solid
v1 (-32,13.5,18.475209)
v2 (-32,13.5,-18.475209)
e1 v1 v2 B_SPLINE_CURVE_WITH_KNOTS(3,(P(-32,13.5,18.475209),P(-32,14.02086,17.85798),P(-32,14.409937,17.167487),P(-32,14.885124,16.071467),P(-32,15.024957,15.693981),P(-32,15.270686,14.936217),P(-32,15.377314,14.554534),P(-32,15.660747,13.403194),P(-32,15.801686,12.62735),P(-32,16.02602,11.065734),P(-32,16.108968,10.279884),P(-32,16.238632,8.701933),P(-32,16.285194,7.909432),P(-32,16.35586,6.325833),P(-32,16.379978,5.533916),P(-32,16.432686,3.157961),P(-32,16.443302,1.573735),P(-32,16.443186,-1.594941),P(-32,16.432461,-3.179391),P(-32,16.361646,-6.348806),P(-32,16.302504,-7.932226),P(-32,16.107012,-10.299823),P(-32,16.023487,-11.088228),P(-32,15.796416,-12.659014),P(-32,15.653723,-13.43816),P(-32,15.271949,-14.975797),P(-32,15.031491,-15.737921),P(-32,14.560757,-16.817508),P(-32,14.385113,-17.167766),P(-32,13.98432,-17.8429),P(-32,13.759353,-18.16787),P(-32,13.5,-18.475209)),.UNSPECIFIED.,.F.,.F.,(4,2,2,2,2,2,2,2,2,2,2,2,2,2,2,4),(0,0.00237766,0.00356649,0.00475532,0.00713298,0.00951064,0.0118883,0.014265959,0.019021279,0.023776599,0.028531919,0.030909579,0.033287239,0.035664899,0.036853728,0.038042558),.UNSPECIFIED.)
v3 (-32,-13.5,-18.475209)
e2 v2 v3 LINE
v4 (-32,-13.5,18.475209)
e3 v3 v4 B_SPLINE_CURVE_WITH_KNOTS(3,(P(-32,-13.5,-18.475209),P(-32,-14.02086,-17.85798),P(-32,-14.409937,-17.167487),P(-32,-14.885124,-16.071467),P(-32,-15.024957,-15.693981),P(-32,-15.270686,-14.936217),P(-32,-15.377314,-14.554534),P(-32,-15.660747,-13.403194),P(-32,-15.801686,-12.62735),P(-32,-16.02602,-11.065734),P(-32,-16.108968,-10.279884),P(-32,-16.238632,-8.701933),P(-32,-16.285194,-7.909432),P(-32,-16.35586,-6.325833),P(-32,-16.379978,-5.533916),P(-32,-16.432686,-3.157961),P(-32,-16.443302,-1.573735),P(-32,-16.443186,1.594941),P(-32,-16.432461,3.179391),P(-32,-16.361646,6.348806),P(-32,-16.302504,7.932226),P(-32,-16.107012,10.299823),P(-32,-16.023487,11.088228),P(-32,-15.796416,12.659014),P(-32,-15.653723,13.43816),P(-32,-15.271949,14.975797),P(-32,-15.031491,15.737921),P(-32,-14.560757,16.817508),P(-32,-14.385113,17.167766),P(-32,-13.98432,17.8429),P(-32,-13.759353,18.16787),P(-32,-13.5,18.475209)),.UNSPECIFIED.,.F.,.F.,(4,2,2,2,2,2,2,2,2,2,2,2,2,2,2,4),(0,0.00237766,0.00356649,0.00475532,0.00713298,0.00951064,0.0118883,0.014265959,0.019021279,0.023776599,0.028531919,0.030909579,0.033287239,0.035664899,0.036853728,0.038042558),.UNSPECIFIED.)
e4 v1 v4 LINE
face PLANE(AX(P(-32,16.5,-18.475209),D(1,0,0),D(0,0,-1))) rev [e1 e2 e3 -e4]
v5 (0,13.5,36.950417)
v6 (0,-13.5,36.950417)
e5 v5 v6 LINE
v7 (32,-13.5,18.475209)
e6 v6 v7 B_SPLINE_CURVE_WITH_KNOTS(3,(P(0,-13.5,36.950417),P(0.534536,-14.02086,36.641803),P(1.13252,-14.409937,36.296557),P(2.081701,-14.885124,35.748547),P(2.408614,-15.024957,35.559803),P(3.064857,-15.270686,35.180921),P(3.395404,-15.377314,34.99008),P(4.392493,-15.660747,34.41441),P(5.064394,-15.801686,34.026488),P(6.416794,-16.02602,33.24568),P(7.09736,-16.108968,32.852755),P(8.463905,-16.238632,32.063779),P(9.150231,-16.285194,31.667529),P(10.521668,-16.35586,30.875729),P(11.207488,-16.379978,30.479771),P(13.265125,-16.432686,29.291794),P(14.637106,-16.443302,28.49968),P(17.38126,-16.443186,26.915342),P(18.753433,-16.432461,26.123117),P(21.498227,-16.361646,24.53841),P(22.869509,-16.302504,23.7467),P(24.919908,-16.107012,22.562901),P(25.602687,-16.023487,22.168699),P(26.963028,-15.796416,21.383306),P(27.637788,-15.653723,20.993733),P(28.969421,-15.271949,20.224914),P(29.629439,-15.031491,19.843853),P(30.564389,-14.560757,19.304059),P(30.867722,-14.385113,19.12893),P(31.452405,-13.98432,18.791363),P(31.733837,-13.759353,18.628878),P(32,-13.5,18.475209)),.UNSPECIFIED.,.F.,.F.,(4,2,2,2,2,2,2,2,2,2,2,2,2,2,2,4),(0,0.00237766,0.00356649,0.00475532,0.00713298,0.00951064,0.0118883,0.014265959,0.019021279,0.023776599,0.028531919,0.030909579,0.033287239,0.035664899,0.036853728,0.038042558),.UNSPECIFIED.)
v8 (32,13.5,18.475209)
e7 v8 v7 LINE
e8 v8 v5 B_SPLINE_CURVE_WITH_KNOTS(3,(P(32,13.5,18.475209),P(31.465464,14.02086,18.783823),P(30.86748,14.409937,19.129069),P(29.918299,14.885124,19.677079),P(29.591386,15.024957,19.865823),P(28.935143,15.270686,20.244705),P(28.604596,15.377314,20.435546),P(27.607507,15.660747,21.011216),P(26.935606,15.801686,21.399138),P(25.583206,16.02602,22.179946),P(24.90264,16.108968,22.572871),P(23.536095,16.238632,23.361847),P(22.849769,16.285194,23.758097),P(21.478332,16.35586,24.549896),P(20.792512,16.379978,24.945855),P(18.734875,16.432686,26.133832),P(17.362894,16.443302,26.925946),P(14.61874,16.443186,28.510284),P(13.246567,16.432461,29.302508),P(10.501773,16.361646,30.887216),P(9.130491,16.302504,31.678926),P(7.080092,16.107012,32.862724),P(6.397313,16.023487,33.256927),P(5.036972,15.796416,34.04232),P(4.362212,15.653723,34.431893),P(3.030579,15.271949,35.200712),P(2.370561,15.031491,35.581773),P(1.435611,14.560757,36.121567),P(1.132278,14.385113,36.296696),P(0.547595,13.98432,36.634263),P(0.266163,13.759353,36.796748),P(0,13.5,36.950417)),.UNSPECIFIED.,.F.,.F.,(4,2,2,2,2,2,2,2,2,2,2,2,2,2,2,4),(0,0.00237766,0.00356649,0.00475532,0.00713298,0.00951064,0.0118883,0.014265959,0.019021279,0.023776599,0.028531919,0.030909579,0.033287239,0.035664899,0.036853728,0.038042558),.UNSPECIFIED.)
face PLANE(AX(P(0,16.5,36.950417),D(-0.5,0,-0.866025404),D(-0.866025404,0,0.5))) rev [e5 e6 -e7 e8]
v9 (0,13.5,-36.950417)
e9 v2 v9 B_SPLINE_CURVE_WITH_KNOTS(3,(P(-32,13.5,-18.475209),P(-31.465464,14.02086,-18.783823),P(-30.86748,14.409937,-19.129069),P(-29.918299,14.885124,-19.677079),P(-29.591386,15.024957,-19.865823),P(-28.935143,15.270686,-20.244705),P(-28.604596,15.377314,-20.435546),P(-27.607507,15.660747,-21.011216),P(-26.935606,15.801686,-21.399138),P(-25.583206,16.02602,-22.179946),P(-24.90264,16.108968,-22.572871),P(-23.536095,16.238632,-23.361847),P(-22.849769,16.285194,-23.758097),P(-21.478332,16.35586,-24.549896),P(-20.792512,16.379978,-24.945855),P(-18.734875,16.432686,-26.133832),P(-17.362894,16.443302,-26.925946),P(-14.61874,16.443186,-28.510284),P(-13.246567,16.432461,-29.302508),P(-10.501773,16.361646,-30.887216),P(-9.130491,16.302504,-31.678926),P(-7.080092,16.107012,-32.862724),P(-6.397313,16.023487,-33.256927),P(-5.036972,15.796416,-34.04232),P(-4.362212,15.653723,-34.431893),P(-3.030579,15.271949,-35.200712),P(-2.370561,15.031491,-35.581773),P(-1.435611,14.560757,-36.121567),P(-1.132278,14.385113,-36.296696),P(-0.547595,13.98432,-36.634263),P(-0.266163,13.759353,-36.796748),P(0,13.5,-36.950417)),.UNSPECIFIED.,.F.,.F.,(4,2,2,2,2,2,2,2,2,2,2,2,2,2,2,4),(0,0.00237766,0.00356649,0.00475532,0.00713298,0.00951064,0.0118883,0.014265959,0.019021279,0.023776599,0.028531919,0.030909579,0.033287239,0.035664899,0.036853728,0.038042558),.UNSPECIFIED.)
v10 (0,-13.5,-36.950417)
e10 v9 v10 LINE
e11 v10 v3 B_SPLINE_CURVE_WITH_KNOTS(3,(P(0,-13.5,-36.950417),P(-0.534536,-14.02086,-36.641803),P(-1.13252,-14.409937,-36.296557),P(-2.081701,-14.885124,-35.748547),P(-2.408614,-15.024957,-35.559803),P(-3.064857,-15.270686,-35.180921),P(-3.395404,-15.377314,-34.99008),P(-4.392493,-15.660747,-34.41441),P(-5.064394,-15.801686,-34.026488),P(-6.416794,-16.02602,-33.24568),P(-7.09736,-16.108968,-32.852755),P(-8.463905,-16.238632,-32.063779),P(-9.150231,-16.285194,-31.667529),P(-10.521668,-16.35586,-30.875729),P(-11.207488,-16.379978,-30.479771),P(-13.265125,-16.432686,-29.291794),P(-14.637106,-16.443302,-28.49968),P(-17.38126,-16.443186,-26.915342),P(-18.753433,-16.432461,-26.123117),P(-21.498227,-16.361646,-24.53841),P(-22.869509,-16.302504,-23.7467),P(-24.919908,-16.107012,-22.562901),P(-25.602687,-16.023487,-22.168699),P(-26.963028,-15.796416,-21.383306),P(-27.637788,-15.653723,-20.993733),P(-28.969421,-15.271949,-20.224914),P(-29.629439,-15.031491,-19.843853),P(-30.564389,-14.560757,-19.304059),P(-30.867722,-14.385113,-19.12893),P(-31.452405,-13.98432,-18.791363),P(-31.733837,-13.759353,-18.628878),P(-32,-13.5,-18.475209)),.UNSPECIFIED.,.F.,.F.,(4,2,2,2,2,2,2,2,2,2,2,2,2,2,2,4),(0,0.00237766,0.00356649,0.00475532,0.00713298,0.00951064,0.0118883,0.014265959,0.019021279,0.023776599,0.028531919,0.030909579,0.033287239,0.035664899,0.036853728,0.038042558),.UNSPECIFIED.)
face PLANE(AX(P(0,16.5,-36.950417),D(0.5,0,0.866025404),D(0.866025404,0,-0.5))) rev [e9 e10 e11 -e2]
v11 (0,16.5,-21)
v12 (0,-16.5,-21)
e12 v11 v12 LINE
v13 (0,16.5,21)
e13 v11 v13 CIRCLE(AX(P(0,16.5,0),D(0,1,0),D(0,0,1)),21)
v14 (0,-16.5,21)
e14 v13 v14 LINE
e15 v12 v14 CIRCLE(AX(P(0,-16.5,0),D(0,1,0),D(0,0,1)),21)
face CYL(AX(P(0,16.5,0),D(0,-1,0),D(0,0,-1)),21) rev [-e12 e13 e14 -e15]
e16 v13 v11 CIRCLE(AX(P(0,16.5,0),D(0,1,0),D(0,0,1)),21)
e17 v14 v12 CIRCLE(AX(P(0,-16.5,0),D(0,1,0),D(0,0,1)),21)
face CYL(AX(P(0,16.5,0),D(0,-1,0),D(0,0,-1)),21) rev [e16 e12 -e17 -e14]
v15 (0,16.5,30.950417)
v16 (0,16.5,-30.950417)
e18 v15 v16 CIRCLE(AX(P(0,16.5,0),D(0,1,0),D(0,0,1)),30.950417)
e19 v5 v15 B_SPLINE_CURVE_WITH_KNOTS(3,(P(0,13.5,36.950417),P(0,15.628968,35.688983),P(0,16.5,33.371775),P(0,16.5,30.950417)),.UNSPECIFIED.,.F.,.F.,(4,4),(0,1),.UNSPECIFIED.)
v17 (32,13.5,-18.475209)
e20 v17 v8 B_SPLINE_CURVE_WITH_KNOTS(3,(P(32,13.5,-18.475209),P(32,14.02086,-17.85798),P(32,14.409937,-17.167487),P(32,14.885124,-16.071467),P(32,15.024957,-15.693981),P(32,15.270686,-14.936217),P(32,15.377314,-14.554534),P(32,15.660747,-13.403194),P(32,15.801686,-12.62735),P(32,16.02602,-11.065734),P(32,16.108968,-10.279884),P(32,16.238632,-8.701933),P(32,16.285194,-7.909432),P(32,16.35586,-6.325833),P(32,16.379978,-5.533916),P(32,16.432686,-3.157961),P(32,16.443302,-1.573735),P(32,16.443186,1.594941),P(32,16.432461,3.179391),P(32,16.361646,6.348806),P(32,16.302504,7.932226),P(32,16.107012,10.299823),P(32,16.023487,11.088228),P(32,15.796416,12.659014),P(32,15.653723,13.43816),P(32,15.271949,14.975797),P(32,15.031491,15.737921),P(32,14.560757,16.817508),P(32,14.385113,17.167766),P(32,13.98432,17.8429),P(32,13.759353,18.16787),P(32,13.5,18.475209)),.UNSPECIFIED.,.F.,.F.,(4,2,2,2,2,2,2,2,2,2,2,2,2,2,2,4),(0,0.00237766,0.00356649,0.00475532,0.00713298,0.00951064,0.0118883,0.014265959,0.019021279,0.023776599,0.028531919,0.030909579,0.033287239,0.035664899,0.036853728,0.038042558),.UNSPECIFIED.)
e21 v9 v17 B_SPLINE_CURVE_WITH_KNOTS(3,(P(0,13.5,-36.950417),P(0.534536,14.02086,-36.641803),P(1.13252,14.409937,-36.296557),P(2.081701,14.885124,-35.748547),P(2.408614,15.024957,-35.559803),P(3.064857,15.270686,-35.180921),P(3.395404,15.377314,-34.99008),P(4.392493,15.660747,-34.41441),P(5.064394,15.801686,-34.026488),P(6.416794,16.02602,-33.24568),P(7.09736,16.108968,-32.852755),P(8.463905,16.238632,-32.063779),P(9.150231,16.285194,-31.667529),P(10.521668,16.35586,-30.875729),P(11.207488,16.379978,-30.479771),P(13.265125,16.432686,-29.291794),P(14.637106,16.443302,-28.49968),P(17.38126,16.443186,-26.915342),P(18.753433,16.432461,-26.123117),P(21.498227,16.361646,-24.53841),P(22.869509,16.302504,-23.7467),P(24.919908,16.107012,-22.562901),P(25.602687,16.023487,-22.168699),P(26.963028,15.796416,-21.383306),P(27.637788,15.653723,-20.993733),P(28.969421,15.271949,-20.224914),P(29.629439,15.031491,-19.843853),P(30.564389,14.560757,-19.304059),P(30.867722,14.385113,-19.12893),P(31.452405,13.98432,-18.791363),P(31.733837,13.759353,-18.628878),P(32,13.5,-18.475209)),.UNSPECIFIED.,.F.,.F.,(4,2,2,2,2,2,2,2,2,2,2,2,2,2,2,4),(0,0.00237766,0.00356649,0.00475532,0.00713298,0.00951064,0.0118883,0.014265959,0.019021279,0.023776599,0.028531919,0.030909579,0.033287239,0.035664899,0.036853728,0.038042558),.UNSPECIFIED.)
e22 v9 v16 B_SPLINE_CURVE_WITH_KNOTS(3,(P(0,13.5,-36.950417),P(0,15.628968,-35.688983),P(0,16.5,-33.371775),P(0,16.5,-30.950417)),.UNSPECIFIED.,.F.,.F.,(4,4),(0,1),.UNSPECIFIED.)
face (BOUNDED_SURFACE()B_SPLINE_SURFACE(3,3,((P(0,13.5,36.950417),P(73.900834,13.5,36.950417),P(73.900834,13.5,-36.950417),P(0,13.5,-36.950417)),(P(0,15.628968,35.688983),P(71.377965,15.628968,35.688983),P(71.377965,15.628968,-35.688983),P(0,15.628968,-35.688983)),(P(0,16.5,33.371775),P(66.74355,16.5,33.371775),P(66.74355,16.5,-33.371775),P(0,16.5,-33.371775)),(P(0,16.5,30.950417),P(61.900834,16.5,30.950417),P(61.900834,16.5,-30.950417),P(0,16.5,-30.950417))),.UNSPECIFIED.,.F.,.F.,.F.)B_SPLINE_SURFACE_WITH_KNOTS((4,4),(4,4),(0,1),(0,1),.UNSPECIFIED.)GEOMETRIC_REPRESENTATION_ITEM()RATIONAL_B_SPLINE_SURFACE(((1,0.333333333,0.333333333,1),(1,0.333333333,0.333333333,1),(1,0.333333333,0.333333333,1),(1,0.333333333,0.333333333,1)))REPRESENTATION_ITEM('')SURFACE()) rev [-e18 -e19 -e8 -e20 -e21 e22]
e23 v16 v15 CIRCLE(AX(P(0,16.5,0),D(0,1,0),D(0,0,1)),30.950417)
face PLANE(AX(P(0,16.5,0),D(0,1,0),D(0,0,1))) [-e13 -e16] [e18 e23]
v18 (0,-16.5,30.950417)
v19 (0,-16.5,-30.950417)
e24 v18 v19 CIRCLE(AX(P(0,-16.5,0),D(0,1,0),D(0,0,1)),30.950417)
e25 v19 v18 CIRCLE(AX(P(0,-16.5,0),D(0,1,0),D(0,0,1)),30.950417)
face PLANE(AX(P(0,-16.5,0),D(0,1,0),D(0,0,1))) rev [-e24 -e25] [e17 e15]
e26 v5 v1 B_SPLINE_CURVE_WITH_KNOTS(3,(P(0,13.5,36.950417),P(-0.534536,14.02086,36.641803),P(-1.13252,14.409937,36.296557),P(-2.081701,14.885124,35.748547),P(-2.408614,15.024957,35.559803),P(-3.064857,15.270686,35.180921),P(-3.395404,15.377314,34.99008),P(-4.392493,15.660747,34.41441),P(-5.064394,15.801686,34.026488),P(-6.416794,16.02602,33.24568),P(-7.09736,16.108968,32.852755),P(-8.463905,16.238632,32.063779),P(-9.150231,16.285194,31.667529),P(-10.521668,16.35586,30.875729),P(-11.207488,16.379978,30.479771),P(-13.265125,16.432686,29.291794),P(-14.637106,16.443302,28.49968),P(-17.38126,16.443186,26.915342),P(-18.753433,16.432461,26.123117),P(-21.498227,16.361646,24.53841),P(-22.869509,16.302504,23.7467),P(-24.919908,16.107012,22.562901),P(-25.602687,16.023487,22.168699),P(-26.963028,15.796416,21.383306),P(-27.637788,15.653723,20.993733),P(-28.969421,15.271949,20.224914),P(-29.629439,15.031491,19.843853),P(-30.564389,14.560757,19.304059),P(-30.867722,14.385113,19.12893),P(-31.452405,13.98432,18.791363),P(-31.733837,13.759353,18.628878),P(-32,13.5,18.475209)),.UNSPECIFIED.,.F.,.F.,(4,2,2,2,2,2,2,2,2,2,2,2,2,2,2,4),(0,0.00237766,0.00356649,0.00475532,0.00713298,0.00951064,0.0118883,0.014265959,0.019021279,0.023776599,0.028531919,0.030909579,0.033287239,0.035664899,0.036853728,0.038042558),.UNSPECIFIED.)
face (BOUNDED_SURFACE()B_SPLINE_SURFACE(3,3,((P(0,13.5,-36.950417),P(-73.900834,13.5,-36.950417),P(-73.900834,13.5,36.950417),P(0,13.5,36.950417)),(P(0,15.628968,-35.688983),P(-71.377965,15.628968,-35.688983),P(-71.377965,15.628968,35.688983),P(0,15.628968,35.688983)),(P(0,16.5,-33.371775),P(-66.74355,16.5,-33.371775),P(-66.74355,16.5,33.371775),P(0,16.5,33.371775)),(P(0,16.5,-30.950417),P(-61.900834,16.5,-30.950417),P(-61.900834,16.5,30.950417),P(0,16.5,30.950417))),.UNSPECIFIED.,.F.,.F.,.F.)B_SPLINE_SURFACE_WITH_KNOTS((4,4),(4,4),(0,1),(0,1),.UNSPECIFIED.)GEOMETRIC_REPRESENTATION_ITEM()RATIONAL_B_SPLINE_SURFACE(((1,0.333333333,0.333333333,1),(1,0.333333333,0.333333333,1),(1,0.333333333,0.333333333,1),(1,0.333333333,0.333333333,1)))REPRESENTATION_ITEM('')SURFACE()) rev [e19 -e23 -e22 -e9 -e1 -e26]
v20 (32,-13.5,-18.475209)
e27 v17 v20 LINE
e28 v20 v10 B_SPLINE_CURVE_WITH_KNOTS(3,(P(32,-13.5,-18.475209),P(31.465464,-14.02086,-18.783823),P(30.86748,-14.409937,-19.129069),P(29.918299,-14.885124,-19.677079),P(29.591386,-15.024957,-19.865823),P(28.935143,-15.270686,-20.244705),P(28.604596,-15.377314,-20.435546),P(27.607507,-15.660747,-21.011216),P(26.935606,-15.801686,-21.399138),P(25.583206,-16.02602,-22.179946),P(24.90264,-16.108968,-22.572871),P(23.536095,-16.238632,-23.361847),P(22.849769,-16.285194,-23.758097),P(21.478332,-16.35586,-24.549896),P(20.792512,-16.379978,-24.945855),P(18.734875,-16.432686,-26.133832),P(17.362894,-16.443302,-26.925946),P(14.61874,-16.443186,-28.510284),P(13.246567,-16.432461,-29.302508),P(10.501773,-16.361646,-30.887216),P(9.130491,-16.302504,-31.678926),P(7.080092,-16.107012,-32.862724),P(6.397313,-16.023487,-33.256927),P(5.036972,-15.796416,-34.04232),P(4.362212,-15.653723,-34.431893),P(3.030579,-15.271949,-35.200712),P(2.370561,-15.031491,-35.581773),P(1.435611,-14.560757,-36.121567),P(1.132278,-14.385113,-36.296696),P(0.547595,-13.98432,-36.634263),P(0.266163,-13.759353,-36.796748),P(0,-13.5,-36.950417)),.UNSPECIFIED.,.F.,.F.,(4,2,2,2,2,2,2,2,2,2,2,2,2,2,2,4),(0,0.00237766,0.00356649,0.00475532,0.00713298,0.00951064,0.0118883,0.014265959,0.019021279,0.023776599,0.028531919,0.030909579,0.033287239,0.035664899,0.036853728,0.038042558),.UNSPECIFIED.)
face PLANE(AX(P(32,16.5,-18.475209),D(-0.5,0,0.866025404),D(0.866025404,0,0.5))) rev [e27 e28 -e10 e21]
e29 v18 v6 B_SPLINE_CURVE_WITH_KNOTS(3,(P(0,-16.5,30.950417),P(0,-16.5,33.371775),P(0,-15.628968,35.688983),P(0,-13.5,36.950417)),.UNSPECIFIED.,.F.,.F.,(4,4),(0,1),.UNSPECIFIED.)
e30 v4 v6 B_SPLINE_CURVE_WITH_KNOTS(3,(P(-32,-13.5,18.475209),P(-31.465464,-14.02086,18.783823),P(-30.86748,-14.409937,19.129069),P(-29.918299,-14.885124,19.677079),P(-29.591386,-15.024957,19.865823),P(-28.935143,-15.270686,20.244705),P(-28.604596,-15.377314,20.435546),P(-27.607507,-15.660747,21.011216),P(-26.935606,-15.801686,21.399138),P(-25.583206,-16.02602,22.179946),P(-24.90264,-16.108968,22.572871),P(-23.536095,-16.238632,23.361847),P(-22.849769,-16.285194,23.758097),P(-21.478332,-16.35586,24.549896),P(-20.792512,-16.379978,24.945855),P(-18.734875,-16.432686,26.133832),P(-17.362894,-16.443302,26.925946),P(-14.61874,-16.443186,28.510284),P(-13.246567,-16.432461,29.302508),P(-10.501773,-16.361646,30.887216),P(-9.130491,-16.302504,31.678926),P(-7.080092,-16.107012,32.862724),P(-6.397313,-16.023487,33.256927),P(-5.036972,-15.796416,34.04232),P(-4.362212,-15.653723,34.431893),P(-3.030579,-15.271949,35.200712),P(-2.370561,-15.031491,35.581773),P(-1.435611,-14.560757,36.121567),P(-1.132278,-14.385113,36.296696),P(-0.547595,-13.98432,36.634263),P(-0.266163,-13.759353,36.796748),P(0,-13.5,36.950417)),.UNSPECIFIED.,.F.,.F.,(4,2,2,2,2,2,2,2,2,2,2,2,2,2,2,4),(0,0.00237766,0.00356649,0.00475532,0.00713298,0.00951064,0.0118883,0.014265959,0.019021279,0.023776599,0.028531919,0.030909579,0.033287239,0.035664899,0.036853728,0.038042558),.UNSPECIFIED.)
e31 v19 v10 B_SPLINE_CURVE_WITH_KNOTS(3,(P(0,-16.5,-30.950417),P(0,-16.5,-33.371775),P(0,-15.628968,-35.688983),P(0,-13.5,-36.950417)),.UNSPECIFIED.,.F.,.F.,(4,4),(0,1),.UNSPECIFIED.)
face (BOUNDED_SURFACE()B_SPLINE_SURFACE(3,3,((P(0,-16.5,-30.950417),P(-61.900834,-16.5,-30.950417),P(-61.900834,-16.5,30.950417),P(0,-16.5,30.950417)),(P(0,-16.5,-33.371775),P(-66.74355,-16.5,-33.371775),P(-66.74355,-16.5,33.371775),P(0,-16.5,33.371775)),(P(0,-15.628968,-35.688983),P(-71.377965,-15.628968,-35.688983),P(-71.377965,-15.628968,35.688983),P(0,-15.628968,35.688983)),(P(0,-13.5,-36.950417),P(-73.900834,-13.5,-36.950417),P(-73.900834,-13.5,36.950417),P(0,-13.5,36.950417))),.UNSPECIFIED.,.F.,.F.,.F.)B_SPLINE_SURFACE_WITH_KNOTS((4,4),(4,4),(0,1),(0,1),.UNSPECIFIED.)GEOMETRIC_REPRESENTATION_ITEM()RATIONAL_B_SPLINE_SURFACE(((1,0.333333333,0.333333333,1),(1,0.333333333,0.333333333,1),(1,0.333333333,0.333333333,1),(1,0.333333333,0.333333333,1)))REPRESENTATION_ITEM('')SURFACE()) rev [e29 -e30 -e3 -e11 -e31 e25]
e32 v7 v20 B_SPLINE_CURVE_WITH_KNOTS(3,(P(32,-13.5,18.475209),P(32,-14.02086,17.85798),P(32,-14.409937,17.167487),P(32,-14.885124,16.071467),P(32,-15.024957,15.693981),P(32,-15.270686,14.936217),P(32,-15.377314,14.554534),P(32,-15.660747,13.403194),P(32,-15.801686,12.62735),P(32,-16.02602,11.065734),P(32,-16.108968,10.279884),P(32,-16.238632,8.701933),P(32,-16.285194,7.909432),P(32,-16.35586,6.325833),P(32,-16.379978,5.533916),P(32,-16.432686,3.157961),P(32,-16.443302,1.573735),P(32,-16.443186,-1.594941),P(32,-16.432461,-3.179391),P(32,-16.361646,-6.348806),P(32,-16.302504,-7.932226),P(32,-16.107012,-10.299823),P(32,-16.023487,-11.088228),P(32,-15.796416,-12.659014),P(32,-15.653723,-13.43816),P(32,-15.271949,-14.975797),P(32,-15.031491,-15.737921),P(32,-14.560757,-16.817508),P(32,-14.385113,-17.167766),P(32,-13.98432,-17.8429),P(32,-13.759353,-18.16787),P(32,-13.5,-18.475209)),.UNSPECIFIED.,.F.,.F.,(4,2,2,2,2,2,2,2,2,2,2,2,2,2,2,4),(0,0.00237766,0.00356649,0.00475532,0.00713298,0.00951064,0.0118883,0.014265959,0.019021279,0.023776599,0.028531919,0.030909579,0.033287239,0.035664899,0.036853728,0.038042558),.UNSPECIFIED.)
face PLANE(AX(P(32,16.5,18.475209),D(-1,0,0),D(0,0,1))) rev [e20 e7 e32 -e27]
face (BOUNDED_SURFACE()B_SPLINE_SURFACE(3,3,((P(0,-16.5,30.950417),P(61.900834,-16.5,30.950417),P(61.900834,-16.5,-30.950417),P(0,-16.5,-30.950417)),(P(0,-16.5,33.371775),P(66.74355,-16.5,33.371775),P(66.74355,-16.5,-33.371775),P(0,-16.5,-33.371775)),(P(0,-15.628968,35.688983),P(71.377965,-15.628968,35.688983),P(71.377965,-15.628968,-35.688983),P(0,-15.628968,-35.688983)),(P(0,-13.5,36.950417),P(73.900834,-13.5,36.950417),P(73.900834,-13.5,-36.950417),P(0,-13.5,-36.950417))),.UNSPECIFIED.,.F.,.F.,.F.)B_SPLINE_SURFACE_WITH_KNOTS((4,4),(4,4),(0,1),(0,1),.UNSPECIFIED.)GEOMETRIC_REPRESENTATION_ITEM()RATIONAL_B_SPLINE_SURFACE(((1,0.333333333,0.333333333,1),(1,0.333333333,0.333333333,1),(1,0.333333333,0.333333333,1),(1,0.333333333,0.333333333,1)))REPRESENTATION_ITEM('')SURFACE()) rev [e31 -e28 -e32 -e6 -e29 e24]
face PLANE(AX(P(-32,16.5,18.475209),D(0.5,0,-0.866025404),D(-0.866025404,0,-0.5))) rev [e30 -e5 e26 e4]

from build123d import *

# Parameters (mm, degrees)
SKETCH_1_R           = 21
BOSS_EXTRUDE_1_DEPTH = 16.5


with BuildPart() as part:
    # Sketch 1 → Boss-Extrude 1 (new, symmetric)
    with BuildSketch(Plane(origin=(0, 0, 0), x_dir=(1, 0, 0), z_dir=(0, 1, 0))):
        Polygon((0, 36.950417228), (-32, 18.475208614), (-32, -18.475208614), (0, -36.950417228), (32, -18.475208614), (32, 18.475208614), align=None)
        with Locations(Location((0, 0, 0), (0, 0, 270))):
            Circle(SKETCH_1_R, mode=Mode.SUBTRACT)
    extrude(amount=BOSS_EXTRUDE_1_DEPTH, both=True)

    # Sketch 2 → Cut-Revolve 1 (revolve, cut)
    with BuildSketch(Plane(origin=(0, 0, 0), x_dir=(0, 0, -1), z_dir=(1, 0, 0))):
        with BuildLine():
            Line((-30.950417228, 16.5), (-36.950417228, 16.5))
            Line((-36.950417228, 16.5), (-36.950417228, 13.5))
            add(Edge.make_bspline(
                [(-36.950417228, 13.5), (-35.688982599, 15.62896823), (-33.371774895, 16.5), (-30.950417228, 16.5)],
                knots=[0, 0, 0, 0, 1, 1, 1, 1], degree=3))
        make_face()
        with BuildLine():
            Line((-36.950417228, -16.5), (-36.950417228, -13.5))
            add(Edge.make_bspline(
                [(-36.950417228, -13.5), (-35.688982599, -15.62896823), (-33.371774895, -16.5), (-30.950417228, -16.5)],
                knots=[0, 0, 0, 0, 1, 1, 1, 1], degree=3))
            Line((-30.950417228, -16.5), (-36.950417228, -16.5))
        make_face()
    revolve(axis=Axis((0, 20.720193417, 0), (0, -1, 0)), mode=Mode.SUBTRACT)


solid = part.part
